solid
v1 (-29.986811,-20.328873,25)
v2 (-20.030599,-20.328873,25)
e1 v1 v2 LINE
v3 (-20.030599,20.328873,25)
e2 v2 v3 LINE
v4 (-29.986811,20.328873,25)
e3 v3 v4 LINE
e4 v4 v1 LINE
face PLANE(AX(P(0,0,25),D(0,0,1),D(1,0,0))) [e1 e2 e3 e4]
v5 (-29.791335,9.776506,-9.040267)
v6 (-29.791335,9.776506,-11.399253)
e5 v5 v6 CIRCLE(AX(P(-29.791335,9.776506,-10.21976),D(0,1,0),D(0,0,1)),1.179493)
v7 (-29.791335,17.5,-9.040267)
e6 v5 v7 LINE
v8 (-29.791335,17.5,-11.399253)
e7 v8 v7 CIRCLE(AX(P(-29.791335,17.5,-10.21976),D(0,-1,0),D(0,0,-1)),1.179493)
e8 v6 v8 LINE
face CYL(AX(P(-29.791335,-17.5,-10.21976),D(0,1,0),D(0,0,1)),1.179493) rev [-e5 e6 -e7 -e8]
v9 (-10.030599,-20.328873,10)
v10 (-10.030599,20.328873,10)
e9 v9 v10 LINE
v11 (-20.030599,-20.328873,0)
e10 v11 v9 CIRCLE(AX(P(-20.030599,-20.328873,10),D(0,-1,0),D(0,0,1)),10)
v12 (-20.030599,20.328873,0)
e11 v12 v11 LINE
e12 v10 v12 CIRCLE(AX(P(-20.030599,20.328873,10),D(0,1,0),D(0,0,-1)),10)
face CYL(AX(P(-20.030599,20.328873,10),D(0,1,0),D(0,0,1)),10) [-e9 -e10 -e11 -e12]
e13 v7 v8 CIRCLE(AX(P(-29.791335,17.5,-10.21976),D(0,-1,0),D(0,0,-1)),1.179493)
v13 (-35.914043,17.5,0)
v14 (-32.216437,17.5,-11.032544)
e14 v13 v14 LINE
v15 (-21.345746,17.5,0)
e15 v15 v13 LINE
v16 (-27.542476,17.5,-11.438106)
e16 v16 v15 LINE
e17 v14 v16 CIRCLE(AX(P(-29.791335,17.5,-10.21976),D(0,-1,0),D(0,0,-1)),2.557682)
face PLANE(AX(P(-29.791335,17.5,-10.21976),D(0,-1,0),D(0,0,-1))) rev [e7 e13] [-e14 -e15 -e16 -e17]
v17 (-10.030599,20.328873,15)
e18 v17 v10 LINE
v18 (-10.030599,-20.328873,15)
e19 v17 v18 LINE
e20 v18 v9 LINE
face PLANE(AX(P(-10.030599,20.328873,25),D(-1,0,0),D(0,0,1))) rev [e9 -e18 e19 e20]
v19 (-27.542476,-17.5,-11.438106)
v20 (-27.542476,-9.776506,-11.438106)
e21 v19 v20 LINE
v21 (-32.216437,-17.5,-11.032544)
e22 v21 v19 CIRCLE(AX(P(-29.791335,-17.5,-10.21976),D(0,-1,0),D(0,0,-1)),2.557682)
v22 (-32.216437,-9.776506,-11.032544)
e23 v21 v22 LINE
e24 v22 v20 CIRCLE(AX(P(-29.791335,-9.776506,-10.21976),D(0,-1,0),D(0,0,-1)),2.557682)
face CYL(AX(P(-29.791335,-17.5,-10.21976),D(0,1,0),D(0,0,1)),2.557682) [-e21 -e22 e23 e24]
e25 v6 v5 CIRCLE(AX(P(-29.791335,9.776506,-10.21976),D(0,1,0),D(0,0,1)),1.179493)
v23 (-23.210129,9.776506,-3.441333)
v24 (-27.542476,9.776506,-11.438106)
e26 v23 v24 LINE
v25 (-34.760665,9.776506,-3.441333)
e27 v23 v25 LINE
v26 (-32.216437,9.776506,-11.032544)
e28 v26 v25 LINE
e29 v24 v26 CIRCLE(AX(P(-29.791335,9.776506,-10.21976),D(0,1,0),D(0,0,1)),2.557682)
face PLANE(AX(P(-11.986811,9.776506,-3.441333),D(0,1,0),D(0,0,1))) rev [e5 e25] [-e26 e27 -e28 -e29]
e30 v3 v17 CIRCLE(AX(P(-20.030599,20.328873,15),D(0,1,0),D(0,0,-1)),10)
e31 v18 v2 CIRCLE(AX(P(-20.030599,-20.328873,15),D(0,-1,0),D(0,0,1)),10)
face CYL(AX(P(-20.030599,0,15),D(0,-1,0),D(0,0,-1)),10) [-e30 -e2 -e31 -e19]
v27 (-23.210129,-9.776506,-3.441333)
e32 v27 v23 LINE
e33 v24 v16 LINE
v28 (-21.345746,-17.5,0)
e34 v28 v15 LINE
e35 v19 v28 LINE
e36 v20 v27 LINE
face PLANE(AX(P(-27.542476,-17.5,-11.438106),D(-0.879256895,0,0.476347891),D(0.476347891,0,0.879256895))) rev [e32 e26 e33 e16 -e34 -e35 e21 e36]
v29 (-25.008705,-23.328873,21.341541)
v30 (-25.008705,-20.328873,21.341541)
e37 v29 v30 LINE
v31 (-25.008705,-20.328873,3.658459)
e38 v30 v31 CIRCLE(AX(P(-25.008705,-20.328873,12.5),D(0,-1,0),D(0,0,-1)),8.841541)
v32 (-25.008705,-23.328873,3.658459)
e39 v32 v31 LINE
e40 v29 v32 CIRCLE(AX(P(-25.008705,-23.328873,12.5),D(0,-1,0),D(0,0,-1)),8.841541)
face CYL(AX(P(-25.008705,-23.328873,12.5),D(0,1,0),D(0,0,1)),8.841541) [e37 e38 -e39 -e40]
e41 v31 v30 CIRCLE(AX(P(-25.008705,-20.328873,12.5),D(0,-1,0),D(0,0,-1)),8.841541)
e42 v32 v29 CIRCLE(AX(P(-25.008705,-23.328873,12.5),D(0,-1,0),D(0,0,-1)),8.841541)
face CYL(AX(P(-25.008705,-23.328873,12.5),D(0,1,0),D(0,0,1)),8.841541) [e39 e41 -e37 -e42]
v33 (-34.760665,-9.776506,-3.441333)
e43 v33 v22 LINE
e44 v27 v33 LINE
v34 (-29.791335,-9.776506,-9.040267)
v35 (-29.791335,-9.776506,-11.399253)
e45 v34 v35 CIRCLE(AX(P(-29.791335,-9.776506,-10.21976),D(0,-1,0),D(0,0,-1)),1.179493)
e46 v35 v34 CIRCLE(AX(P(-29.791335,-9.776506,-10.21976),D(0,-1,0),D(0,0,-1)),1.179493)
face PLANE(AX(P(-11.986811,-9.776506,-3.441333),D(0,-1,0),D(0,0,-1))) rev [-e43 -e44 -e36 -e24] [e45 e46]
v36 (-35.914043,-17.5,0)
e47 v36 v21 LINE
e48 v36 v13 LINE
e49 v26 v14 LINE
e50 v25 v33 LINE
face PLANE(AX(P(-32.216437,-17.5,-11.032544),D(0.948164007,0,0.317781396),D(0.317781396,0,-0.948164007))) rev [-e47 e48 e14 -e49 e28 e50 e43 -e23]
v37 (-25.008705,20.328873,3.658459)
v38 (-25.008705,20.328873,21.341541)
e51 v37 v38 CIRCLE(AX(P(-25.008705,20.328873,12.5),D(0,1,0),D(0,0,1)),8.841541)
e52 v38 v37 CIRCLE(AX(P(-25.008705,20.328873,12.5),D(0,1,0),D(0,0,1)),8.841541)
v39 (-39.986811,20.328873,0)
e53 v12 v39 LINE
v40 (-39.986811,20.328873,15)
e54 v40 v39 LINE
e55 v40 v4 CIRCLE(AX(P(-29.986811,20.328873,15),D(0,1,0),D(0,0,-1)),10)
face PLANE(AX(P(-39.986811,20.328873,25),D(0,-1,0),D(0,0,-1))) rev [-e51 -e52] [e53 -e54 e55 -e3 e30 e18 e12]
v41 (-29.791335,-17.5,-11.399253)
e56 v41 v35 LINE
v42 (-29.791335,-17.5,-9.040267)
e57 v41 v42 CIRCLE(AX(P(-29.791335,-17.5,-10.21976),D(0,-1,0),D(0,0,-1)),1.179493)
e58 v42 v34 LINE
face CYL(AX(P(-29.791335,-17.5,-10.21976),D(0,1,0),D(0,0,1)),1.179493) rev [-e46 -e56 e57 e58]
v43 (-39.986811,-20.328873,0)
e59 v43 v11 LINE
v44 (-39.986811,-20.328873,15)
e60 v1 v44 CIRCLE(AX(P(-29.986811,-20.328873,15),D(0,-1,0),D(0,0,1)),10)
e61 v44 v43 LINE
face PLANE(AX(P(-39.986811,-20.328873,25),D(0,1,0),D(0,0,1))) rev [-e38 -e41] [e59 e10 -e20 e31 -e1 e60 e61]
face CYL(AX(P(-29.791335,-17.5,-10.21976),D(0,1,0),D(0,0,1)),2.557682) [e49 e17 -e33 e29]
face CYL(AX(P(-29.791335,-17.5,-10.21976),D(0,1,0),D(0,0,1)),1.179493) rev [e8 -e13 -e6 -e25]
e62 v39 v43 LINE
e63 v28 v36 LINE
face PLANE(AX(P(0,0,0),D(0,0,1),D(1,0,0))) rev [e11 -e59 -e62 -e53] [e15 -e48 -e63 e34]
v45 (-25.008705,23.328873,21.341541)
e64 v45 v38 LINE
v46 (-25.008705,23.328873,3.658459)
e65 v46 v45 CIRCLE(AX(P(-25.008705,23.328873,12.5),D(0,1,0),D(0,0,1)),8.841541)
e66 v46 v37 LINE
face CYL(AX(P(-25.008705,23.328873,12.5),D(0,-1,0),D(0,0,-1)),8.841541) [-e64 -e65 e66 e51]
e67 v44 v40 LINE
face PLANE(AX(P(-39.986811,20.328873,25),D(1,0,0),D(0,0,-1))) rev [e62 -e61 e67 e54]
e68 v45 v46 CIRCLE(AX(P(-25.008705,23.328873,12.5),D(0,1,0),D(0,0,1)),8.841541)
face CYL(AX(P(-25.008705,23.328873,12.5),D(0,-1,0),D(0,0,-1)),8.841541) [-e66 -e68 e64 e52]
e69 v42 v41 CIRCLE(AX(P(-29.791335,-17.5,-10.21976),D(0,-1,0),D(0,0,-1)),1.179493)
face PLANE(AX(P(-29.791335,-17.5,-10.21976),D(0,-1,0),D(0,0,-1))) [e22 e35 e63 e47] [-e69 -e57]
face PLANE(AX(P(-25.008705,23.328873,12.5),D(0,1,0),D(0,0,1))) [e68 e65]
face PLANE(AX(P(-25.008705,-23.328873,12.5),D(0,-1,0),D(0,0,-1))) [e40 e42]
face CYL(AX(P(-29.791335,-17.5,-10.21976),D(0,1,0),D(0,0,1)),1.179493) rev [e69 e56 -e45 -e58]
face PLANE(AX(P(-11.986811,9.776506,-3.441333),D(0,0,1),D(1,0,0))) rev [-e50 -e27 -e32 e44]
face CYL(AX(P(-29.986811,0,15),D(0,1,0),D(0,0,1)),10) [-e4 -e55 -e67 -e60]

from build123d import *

# Parameters (mm, degrees)
SKETCH1_W           = 29.956211672
SKETCH1_H           = 40.65774509
BOSS_EXTRUDE1_DEPTH = 25
SKETCH2_R           = 1.179493096
BOSS_EXTRUDE2_DEPTH = 17.5
FILLET1_R           = 10
SKETCH3_R           = 8.841541065
BOSS_EXTRUDE3_DEPTH = 3
BOSS_EXTRUDE4_START = 3
SKETCH4_R           = 8.841541065
BOSS_EXTRUDE4_DEPTH = 3
SKETCH5_W           = 18.672217178
SKETCH5_H           = 19.553012946
CUT_EXTRUDE1_DEPTH  = 28


with BuildPart() as part:
    # Sketch1 → Boss-Extrude1 (new body)
    with BuildSketch(Plane.XY):
        with Locations((-25.008704873, 0)):
            Rectangle(SKETCH1_W, SKETCH1_H)
    extrude(amount=BOSS_EXTRUDE1_DEPTH)

    # Sketch2 → Boss-Extrude2 (add, symmetric)
    with BuildSketch(Plane(origin=(0, 0, -4), x_dir=(1, 0, 0), z_dir=(0, -1, 0))):
        with BuildLine():
            Line((-32.216437007, -7.03254357), (-35.914043193, 4))
            Line((-35.914043193, 4), (-21.345745646, 4))
            Line((-21.345745646, 4), (-27.542475863, -7.438106205))
            ThreePointArc((-27.542475863, -7.438106205), (-30.012436117, -8.767867117), (-32.216437007, -7.03254357))
        make_face()
        with Locations(Location((-29.791335202, -6.219759883, 0), (0, 0, 270))):
            Circle(SKETCH2_R, mode=Mode.SUBTRACT)
    extrude(amount=BOSS_EXTRUDE2_DEPTH, both=True)

    # Fillet1
    fillet1_edges = [part.edges().sort_by_distance(p)[0] for p in [
        (-39.986810709, 0, 25),
        (-10.030599037, 0, 25),
        (-10.030599037, 0, 0),
    ]]
    fillet(fillet1_edges, radius=FILLET1_R)

    # Sketch3 → Boss-Extrude3 (add)
    with BuildSketch(Plane(origin=(0, -20.328872545, 0), x_dir=(-1, 0, 0), z_dir=(0, -1, 0))):
        with Locations(Location((25.008704873, -12.5, 0), (0, 0, 90))):
            Circle(SKETCH3_R)
    extrude(amount=BOSS_EXTRUDE3_DEPTH)

    # Sketch4 → Boss-Extrude4 (add)
    with BuildSketch(Plane(origin=(0, 20.328872545, 0), x_dir=(1, 0, 0), z_dir=(0, 1, 0)).offset(BOSS_EXTRUDE4_START)):
        with Locations(Location((-25.008704873, -12.5, 0), (0, 0, 90))):
            Circle(SKETCH4_R)
    extrude(amount=-BOSS_EXTRUDE4_DEPTH)

    # Sketch5 → Cut-Extrude1 (cut)
    with BuildSketch(Plane.ZY.offset(39.986810709)):
        with Locations((-12.777441663, 0)):
            Rectangle(SKETCH5_W, SKETCH5_H)
    extrude(amount=-CUT_EXTRUDE1_DEPTH, mode=Mode.SUBTRACT)


solid = part.part
